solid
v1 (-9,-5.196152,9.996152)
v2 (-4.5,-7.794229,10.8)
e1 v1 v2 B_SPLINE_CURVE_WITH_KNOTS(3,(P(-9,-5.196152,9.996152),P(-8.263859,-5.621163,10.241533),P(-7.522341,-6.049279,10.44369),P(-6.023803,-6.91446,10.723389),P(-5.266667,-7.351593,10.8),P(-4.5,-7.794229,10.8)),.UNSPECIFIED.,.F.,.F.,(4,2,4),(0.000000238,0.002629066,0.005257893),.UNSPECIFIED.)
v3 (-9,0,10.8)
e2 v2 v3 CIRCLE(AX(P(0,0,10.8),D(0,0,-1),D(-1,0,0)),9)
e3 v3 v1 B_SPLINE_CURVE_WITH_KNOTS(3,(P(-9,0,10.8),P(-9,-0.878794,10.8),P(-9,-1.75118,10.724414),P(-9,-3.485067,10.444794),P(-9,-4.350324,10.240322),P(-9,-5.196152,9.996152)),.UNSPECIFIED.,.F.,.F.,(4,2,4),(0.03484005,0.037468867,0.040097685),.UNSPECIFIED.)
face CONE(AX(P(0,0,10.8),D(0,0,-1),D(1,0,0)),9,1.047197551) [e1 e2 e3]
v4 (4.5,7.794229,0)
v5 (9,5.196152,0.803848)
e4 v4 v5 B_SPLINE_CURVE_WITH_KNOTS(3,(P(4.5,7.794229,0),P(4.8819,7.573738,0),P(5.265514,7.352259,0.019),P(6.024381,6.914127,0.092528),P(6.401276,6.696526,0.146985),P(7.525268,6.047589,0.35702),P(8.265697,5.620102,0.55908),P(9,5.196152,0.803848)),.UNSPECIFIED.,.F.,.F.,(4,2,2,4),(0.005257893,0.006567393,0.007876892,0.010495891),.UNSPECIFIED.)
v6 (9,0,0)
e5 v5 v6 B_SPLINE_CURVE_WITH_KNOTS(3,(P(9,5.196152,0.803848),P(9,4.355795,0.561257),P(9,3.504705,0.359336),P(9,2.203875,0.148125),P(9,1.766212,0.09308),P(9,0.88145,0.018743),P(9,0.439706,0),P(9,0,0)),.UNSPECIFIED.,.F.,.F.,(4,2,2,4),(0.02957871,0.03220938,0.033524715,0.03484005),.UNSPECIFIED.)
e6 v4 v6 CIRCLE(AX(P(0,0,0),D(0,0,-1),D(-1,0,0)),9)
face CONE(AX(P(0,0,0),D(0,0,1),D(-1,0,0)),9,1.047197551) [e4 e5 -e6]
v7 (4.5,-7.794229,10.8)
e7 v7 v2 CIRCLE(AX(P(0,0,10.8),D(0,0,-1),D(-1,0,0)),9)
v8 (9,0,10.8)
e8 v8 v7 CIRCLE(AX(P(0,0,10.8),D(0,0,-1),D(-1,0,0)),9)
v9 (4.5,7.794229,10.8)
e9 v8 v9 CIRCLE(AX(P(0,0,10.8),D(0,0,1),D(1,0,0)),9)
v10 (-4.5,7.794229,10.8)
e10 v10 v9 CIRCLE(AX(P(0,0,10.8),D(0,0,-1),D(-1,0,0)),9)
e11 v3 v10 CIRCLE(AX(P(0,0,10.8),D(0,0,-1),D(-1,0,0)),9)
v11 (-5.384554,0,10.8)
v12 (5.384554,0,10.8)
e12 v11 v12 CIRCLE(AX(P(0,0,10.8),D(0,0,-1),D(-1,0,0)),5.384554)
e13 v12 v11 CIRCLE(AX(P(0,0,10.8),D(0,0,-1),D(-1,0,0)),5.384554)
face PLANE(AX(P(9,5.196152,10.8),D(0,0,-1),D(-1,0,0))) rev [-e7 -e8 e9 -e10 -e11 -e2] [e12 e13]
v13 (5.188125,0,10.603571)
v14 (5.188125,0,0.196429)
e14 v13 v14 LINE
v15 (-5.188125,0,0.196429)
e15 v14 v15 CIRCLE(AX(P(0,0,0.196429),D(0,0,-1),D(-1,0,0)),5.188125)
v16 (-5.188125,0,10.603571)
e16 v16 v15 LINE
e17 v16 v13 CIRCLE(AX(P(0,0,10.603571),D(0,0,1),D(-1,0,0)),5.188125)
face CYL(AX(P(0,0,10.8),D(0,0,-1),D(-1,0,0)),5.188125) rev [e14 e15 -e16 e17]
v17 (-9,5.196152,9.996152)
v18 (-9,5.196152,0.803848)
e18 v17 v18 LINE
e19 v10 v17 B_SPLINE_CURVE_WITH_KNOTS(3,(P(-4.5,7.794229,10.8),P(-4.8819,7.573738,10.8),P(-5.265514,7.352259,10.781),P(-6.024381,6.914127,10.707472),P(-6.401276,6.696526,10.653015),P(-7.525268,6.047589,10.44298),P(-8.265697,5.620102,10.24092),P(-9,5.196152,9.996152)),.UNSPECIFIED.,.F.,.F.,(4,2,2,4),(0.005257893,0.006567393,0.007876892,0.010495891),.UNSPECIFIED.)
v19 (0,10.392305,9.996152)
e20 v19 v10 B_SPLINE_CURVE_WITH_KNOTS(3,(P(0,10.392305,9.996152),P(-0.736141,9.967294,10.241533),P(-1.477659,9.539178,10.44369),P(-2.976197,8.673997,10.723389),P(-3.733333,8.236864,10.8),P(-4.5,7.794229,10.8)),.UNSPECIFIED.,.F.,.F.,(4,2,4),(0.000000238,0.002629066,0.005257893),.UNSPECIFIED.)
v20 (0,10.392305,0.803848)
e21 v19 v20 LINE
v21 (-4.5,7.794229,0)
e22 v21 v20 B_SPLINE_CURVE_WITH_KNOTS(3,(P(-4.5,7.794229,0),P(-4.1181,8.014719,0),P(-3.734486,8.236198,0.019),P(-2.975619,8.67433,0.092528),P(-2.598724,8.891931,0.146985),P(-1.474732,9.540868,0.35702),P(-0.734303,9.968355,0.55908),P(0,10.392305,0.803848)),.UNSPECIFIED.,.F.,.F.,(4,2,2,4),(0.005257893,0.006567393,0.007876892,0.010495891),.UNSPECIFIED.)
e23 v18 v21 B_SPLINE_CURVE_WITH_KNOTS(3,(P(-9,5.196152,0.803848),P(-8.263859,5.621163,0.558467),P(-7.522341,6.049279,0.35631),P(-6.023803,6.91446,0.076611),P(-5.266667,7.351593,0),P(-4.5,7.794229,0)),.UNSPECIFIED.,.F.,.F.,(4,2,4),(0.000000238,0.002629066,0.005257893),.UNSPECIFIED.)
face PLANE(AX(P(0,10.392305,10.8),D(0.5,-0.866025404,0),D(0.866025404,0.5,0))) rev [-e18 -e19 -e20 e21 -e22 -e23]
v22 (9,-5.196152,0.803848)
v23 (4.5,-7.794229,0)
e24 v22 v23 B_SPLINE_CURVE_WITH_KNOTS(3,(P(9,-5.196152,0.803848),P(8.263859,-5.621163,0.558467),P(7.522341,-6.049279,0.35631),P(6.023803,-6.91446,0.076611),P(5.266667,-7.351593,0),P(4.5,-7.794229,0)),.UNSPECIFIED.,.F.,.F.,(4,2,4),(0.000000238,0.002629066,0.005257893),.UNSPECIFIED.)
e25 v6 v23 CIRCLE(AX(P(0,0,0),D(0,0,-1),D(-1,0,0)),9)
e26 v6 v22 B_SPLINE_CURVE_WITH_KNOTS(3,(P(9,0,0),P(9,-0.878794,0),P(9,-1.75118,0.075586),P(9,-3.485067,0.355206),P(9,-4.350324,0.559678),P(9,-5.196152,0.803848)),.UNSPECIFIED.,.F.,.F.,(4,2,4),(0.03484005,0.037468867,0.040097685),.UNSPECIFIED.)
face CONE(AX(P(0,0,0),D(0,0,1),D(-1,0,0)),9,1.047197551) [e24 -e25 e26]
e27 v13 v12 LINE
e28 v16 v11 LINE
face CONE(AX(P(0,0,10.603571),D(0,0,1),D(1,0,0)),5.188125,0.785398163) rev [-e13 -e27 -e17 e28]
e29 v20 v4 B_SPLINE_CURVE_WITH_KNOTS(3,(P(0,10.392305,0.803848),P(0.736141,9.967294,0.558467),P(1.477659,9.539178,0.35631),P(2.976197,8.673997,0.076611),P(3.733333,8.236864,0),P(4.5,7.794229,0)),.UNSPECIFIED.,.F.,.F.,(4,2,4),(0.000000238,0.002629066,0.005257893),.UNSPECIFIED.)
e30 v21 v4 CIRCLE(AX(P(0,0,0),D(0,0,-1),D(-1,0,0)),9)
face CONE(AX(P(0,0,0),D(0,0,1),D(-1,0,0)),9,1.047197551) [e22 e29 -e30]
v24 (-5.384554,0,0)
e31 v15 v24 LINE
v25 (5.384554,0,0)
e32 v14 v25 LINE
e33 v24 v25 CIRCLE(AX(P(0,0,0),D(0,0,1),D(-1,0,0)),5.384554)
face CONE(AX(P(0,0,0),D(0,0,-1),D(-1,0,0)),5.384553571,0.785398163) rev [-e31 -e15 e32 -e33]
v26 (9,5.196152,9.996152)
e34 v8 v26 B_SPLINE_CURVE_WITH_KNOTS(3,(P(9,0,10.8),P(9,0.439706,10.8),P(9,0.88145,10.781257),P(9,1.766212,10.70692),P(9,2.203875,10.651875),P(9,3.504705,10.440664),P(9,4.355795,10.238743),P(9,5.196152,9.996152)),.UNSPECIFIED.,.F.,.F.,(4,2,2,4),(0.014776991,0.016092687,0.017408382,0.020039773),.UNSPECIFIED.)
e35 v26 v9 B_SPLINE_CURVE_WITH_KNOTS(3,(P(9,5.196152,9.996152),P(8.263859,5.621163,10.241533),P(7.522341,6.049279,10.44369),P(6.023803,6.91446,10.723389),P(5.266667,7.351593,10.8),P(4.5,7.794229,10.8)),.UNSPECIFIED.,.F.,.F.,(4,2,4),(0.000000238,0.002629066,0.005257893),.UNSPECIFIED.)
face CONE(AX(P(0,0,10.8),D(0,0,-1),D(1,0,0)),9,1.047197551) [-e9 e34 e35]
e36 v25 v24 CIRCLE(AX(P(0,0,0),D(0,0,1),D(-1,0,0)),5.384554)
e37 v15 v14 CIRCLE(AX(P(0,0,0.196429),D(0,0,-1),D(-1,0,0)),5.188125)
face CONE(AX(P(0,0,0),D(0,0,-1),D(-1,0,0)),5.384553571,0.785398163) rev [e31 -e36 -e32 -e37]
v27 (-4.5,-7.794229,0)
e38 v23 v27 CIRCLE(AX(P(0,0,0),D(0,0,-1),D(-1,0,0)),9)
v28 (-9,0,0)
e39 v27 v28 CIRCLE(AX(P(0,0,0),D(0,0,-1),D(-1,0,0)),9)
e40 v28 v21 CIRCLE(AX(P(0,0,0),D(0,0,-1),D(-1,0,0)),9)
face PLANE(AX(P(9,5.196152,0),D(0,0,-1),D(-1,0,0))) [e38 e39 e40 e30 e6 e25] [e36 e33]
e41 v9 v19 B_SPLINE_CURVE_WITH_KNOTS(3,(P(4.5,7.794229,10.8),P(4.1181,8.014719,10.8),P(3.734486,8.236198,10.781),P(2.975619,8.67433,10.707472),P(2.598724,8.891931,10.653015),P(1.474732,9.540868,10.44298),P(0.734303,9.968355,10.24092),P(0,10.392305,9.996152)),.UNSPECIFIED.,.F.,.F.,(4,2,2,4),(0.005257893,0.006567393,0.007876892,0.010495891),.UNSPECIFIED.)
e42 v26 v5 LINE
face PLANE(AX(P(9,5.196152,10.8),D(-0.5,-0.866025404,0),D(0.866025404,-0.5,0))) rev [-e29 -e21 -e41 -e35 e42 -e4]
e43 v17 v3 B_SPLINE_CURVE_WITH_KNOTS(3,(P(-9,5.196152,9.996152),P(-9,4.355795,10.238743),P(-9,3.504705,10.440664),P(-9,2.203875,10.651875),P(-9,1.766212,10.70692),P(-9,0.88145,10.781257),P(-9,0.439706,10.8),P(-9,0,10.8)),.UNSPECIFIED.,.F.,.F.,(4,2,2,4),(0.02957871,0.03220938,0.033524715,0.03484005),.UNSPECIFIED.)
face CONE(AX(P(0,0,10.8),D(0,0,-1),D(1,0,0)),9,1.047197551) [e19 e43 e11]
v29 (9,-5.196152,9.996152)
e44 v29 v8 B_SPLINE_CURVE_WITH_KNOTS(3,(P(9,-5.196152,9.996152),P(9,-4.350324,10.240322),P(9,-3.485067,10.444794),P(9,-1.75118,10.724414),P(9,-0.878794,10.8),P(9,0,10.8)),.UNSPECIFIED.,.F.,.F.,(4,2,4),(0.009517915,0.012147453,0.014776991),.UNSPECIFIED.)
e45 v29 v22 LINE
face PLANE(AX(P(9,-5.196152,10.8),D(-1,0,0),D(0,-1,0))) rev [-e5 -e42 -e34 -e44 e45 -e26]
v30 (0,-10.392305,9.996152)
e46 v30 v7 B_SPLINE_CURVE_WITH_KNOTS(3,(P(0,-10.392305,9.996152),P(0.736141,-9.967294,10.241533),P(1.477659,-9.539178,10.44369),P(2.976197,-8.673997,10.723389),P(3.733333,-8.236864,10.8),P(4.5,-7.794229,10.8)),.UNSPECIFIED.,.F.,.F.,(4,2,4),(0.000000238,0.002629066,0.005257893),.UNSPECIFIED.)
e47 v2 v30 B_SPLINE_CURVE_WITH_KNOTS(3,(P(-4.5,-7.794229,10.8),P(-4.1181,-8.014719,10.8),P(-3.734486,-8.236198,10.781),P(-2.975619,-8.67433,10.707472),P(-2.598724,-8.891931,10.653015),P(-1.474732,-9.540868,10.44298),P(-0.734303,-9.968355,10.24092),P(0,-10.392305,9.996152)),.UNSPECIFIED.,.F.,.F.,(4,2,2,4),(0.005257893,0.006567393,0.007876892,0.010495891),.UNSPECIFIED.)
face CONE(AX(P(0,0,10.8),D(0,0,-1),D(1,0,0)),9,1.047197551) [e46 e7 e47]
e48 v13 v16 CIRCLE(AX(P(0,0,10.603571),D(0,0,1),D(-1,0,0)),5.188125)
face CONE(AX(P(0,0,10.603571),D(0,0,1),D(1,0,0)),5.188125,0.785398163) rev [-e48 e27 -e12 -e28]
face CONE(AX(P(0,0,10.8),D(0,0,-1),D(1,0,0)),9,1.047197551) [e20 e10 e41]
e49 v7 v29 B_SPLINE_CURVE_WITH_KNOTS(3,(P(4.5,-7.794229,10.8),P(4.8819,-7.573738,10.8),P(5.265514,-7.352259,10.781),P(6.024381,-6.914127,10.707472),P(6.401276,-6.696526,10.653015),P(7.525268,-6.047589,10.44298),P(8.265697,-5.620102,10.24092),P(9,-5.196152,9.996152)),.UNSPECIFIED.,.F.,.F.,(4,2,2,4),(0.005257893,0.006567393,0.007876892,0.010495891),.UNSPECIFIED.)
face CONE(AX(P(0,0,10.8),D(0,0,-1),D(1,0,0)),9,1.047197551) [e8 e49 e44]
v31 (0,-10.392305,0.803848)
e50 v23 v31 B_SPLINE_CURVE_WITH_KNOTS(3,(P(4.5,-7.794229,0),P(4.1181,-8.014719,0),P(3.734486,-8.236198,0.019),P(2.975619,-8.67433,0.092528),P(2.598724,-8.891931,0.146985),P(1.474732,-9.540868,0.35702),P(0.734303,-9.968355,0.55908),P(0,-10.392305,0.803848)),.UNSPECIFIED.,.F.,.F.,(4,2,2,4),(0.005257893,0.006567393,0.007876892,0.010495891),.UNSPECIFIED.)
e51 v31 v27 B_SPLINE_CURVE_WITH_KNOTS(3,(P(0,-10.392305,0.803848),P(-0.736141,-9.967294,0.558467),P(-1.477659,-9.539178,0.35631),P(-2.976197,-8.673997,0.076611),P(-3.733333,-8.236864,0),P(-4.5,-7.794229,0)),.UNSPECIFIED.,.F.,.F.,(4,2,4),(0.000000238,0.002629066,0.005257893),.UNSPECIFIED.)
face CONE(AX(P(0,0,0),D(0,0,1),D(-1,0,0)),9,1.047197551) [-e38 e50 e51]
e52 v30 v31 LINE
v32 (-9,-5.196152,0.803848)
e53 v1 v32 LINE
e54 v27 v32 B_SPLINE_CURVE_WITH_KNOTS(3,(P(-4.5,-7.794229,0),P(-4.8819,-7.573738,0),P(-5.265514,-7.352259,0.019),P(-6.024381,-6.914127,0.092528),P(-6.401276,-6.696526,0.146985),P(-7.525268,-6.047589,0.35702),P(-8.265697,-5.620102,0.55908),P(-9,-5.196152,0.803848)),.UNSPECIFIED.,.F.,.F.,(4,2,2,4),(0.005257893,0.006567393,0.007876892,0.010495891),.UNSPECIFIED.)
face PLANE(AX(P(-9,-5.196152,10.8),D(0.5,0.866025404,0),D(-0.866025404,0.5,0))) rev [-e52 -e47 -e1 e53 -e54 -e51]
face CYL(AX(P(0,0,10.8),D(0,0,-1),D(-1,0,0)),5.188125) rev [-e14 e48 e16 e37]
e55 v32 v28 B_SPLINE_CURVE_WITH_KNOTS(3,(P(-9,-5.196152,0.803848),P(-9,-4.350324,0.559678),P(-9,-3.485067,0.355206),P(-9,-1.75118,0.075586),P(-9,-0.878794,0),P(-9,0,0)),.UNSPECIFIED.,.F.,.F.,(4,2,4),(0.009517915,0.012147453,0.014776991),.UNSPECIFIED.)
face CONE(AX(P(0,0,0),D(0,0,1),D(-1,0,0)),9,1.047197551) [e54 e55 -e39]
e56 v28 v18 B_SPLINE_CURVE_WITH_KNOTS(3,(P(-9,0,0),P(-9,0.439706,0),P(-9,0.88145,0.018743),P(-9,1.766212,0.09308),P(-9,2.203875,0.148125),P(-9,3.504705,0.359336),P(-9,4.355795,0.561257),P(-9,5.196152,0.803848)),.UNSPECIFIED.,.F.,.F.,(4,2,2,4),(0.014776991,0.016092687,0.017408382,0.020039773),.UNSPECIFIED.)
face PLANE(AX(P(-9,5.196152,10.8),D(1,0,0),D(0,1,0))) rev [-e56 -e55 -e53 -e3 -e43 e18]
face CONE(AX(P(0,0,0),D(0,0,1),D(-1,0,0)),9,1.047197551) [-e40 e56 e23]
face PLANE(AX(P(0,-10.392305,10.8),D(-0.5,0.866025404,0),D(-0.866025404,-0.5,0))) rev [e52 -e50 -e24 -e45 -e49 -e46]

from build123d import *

# Parameters (mm, degrees)
SKETCH_1_R          = 5.188125
EXTRUDE_652_DEPTH   = 10.8
SKETCH_2_OUTSIDE_W  = 89.934
SKETCH_2_OUTSIDE_H  = 92.718
SKETCH_2_OUTSIDE_R  = 9
CUT_EXTRUDE_1_DEPTH = 18.482562741
CUT_EXTRUDE_1_DRAFT = -60
SKETCH_3_OUTSIDE_W  = 89.934
SKETCH_3_OUTSIDE_H  = 92.718
SKETCH_3_OUTSIDE_R  = 9
CUT_EXTRUDE_2_DEPTH = 18.482562741
CUT_EXTRUDE_2_DRAFT = -60
CHAMFER_1_SIZE      = 0.196428571


with BuildPart() as part:
    # 草图1 → Extrude 652 (new body)
    with BuildSketch(Plane.XY):
        Polygon((0, 10.392304845), (-9, 5.196152423), (-9, -5.196152423), (0, -10.392304845), (9, -5.196152423), (9, 5.196152423), align=None)
        with Locations(Location((0, 0, 0), (0, 0, 180))):
            Circle(SKETCH_1_R, mode=Mode.SUBTRACT)
    extrude(amount=EXTRUDE_652_DEPTH)


with BuildPart() as cut_extrude_1_tool:
    # 草图2 outside → 切除-拉伸1 (with draft: the straight prism first)
    with BuildSketch(Plane(origin=(0, 0, 0), x_dir=(-1, 0, 0), z_dir=(0, 0, -1))):
        Rectangle(SKETCH_2_OUTSIDE_W, SKETCH_2_OUTSIDE_H)
        Circle(SKETCH_2_OUTSIDE_R, mode=Mode.SUBTRACT)
    extrude(amount=-CUT_EXTRUDE_1_DEPTH)
    # 切除-拉伸1: the draft: its side faces are tilted about the plane it starts from
    cut_extrude_1_sides = [cut_extrude_1_tool.faces().sort_by_distance(p)[0] for p in [
        (0, -46.359, 9.241281371),
        (-44.967, 0, 9.241281371),
        (0, 46.359, 9.241281371),
        (44.967, 0, 9.241281371),
        (9, 0, 9.241281371),
    ]]
    draft(cut_extrude_1_sides, Plane(origin=(0, 0, 0), x_dir=(-1, 0, 0), z_dir=(0, 0, -1)), CUT_EXTRUDE_1_DRAFT)


with BuildPart() as part_1:
    add(part.part)

    # 切除-拉伸1: cut by cut_extrude_1_tool
    add(cut_extrude_1_tool.part, mode=Mode.SUBTRACT)


with BuildPart() as cut_extrude_2_tool:
    # 草图3 outside → 切除-拉伸2 (with draft: the straight prism first)
    with BuildSketch(Plane.XY.offset(10.8)):
        Rectangle(SKETCH_3_OUTSIDE_W, SKETCH_3_OUTSIDE_H)
        Circle(SKETCH_3_OUTSIDE_R, mode=Mode.SUBTRACT)
    extrude(amount=-CUT_EXTRUDE_2_DEPTH)
    # 切除-拉伸2: the draft: its side faces are tilted about the plane it starts from
    cut_extrude_2_sides = [cut_extrude_2_tool.faces().sort_by_distance(p)[0] for p in [
        (0, -46.359, 1.558718629),
        (44.967, 0, 1.558718629),
        (0, 46.359, 1.558718629),
        (-44.967, 0, 1.558718629),
        (-9, 0, 1.558718629),
    ]]
    draft(cut_extrude_2_sides, Plane.XY.offset(10.8), CUT_EXTRUDE_2_DRAFT)


with BuildPart() as part_2:
    add(part_1.part)

    # 切除-拉伸2: cut by cut_extrude_2_tool
    add(cut_extrude_2_tool.part, mode=Mode.SUBTRACT)

    # 倒角1
    chamfer_1_edges = [part_2.edges().sort_by_distance(p)[0] for p in [
        (5.188125, 0, 0),
        (5.188125, 0, 10.8),
    ]]
    chamfer(chamfer_1_edges, length=CHAMFER_1_SIZE)


solid = part_2.part
